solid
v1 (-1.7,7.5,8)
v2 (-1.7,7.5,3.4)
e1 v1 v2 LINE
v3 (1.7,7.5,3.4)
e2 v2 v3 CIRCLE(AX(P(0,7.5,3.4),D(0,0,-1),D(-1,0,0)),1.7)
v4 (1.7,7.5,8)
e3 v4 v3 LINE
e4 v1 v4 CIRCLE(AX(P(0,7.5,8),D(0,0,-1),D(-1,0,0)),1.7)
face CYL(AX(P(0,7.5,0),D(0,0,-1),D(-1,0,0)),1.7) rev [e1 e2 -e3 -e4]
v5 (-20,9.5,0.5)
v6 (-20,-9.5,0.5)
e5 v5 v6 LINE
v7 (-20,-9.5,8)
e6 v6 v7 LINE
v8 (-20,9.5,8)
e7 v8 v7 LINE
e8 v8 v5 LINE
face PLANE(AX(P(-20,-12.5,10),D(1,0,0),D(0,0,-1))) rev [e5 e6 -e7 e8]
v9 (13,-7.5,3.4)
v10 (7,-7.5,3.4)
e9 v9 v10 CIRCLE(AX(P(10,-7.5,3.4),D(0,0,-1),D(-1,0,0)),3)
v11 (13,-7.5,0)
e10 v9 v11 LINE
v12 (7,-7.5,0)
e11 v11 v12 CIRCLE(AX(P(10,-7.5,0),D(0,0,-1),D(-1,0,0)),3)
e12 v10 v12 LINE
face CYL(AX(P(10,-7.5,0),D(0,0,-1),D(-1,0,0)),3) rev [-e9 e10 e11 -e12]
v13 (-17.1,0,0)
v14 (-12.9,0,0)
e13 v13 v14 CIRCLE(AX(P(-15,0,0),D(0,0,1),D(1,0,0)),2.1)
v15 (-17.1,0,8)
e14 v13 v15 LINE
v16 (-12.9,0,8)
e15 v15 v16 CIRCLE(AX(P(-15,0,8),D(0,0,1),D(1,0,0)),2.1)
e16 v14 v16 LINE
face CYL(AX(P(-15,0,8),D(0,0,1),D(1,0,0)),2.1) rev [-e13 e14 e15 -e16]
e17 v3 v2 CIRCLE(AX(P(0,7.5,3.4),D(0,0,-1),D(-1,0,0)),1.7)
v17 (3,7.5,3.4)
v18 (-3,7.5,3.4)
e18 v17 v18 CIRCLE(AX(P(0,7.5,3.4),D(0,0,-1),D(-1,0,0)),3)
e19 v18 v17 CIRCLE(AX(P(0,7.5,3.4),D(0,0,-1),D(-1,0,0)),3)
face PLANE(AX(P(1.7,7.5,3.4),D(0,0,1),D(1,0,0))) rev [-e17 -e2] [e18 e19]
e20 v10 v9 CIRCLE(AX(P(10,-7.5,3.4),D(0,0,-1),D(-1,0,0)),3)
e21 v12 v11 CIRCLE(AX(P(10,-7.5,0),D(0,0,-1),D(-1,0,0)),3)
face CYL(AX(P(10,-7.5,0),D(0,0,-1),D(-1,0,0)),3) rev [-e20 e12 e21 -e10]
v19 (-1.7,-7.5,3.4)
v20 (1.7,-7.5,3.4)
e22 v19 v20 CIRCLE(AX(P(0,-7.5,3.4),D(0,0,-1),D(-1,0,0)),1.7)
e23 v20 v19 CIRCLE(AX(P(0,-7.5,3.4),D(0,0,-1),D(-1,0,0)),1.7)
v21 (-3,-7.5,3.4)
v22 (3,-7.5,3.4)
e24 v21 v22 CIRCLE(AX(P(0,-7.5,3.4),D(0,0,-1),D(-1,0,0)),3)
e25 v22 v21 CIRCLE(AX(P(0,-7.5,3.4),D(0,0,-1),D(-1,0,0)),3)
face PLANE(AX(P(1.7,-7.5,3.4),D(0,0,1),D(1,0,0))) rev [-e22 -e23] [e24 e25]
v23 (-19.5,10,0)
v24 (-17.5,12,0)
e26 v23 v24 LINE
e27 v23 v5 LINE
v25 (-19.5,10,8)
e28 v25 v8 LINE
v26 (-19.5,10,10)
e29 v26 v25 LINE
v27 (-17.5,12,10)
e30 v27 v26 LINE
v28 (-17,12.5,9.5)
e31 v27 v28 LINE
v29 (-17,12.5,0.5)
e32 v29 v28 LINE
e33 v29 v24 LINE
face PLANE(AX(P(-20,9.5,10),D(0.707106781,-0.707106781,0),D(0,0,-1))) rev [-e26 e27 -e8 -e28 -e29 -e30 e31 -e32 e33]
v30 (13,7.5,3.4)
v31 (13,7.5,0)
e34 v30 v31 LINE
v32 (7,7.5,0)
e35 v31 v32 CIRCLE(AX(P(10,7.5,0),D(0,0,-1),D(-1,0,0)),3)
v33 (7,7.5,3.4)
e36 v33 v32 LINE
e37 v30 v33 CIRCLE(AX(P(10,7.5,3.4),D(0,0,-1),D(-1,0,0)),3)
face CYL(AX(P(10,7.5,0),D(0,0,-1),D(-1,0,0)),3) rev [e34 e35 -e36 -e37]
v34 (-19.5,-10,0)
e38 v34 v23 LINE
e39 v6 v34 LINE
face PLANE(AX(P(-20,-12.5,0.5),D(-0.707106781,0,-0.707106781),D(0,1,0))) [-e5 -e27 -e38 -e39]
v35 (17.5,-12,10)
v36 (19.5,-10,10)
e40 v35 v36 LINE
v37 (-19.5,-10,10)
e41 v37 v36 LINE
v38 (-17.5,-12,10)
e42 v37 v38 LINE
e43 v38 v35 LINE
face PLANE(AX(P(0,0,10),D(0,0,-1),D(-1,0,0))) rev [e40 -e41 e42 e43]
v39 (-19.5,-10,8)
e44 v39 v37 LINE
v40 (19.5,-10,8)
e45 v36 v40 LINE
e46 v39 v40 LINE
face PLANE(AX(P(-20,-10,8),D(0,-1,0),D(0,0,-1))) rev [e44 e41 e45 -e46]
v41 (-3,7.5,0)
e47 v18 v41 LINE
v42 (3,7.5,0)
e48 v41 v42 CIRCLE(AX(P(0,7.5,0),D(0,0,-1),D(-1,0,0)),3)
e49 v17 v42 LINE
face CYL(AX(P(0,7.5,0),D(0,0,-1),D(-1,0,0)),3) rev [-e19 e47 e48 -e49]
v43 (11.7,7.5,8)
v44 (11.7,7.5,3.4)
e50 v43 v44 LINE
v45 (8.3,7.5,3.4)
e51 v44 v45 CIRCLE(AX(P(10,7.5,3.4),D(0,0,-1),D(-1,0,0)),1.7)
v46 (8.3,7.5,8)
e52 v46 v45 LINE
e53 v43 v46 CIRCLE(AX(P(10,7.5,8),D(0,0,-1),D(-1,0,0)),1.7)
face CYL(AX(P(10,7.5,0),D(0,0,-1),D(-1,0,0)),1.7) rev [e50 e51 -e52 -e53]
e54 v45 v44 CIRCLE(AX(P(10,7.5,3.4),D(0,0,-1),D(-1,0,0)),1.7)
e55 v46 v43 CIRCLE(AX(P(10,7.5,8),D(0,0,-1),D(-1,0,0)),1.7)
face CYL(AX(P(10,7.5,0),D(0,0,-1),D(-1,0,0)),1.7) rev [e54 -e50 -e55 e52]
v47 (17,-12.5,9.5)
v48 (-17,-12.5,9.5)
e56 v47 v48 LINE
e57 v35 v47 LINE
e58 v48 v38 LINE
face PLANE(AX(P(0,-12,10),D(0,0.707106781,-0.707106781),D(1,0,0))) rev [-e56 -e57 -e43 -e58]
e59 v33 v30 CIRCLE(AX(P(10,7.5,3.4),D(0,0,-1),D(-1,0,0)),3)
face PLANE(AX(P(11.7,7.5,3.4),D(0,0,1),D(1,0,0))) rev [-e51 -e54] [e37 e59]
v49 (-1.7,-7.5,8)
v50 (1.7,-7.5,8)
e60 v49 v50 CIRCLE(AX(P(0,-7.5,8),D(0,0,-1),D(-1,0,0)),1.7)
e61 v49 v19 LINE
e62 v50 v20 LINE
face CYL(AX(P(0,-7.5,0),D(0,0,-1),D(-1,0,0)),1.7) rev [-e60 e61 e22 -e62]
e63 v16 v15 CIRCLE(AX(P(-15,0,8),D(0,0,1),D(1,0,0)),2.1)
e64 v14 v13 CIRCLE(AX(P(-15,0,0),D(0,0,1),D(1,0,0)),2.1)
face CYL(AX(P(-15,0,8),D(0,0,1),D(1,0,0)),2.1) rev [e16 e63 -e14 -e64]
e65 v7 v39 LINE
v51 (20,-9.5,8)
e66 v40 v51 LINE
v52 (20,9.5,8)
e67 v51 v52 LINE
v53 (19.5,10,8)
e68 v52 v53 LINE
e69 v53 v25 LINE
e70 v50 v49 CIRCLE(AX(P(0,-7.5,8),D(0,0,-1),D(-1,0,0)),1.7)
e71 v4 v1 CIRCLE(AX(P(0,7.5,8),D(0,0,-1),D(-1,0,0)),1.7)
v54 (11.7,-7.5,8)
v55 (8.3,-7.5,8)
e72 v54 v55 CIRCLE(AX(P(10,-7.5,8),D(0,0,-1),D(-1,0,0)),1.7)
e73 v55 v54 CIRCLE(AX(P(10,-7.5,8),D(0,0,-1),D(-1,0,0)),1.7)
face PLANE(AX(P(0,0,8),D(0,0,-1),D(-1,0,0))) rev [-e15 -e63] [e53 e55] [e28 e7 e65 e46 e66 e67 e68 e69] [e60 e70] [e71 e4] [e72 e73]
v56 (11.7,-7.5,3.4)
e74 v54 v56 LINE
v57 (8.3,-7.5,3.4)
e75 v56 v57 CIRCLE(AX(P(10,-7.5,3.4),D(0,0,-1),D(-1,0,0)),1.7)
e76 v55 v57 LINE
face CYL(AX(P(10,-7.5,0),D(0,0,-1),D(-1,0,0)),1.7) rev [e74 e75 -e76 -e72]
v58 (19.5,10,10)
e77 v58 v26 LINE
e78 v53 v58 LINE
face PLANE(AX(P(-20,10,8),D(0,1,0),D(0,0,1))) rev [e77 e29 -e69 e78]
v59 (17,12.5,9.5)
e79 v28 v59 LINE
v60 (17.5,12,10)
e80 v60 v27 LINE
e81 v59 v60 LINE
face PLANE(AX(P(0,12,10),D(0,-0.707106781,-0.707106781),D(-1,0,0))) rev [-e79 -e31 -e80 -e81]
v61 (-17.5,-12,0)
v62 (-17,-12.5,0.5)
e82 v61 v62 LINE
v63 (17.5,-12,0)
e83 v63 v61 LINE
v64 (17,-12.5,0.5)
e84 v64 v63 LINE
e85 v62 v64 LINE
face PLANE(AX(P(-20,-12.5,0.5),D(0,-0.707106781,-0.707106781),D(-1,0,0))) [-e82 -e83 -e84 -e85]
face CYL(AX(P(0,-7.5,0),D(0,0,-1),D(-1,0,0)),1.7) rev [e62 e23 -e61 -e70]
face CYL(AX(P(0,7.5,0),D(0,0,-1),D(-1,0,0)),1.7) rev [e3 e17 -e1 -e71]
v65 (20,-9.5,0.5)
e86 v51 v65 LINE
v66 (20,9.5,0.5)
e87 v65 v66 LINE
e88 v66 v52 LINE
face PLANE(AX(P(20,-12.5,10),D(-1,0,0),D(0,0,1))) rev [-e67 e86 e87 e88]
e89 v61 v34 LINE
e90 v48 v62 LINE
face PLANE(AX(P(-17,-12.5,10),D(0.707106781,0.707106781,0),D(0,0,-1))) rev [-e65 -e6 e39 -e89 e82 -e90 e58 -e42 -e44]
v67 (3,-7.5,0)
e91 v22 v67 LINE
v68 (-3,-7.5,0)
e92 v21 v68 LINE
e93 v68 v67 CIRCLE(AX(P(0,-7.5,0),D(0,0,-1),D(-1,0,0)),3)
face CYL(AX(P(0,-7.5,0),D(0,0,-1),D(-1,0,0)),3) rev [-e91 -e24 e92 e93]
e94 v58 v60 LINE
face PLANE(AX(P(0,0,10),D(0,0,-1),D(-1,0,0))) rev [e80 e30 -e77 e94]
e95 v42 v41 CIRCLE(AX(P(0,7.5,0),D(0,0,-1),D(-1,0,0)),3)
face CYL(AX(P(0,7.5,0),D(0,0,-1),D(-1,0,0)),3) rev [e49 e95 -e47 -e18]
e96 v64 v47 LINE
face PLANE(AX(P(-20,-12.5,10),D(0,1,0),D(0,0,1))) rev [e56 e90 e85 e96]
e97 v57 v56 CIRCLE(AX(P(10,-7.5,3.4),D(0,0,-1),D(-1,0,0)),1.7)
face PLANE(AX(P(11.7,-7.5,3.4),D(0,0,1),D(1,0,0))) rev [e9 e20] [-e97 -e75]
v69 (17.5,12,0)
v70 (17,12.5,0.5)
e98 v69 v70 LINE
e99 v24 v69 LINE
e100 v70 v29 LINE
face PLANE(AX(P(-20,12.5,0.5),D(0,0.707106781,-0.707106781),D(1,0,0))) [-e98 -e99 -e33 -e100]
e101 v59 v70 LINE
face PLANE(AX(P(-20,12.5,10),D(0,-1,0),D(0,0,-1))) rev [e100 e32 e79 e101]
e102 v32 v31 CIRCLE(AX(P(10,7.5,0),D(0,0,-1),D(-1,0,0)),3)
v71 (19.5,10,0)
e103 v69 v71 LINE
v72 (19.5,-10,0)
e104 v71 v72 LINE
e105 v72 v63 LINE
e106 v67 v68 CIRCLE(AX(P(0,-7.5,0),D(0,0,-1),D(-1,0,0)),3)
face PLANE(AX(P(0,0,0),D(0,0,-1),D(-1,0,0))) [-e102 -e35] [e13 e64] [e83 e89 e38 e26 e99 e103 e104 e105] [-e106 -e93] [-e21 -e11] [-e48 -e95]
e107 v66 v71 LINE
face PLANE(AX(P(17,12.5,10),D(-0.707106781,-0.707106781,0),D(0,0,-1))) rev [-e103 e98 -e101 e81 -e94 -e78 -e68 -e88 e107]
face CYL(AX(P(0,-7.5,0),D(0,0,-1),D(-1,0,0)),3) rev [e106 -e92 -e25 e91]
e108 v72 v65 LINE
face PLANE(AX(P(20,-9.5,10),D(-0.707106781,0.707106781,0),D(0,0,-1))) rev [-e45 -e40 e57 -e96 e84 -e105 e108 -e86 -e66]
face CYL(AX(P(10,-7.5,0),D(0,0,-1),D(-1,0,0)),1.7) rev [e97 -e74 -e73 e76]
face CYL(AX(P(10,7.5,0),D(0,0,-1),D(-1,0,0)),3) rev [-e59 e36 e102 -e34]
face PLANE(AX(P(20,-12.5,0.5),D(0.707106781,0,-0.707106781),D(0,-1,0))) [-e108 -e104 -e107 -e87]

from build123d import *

# Parameters (mm, degrees)
SKETCH1_W                                          = 40
SKETCH1_H                                          = 25
BOSS_EXTRUDE1_DEPTH                                = 10
SKETCH2_W                                          = 40
SKETCH2_H                                          = 20
CUT_EXTRUDE1_DEPTH                                 = 2
M5_TAPPED_HOLE1_D                                  = 4.2
HOLE_SIZE_BASED_ON_SOCKET_HEAD_CAP_SCR_D           = 3.4
HOLE_SIZE_BASED_ON_SOCKET_HEAD_CAP_SCR_CBORE_D     = 6
HOLE_SIZE_BASED_ON_SOCKET_HEAD_CAP_SCR_CBORE_DEPTH = 3.4
CHAMFER1_SIZE                                      = 3
CHAMFER2_SIZE                                      = 0.5


with BuildPart() as part:
    # Sketch1 → Boss-Extrude1 (new body)
    with BuildSketch(Plane.XY):
        Rectangle(SKETCH1_W, SKETCH1_H)
    extrude(amount=BOSS_EXTRUDE1_DEPTH)

    # Sketch2 → Cut-Extrude1 (cut)
    with BuildSketch(Plane.XY.offset(10)):
        Rectangle(SKETCH2_W, SKETCH2_H)
    extrude(amount=-CUT_EXTRUDE1_DEPTH, mode=Mode.SUBTRACT)

    # M5 Tapped Hole1 (through all)
    with Locations(Plane.XY.offset(8)):
        with Locations((-15, 0)):
            Hole(M5_TAPPED_HOLE1_D / 2)

    # Hole Size (Based On) Socket Head Cap Screw Type1 (through all)
    with Locations(Plane(origin=(0, 0, 0), x_dir=(-1, 0, 0), z_dir=(0, 0, -1))):
        with Locations((-10, 7.5), (-10, -7.5), (0, 7.5), (0, -7.5)):
            CounterBoreHole(HOLE_SIZE_BASED_ON_SOCKET_HEAD_CAP_SCR_D / 2, HOLE_SIZE_BASED_ON_SOCKET_HEAD_CAP_SCR_CBORE_D / 2, HOLE_SIZE_BASED_ON_SOCKET_HEAD_CAP_SCR_CBORE_DEPTH)

    # Chamfer1
    chamfer1_edges = [part.edges().sort_by_distance(p)[0] for p in [
        (20, -12.5, 5),
        (20, 12.5, 5),
        (-20, -12.5, 5),
        (-20, 12.5, 5),
    ]]
    chamfer(chamfer1_edges, length=CHAMFER1_SIZE)

    # Chamfer2
    chamfer2_edges = [part.edges().sort_by_distance(p)[0] for p in [
        (20, 0, 0),
        (0, -12.5, 0),
        (-20, 0, 0),
        (0, 12.5, 0),
        (0, -12.5, 10),
        (0, 12.5, 10),
    ]]
    chamfer(chamfer2_edges, length=CHAMFER2_SIZE)


solid = part.part
